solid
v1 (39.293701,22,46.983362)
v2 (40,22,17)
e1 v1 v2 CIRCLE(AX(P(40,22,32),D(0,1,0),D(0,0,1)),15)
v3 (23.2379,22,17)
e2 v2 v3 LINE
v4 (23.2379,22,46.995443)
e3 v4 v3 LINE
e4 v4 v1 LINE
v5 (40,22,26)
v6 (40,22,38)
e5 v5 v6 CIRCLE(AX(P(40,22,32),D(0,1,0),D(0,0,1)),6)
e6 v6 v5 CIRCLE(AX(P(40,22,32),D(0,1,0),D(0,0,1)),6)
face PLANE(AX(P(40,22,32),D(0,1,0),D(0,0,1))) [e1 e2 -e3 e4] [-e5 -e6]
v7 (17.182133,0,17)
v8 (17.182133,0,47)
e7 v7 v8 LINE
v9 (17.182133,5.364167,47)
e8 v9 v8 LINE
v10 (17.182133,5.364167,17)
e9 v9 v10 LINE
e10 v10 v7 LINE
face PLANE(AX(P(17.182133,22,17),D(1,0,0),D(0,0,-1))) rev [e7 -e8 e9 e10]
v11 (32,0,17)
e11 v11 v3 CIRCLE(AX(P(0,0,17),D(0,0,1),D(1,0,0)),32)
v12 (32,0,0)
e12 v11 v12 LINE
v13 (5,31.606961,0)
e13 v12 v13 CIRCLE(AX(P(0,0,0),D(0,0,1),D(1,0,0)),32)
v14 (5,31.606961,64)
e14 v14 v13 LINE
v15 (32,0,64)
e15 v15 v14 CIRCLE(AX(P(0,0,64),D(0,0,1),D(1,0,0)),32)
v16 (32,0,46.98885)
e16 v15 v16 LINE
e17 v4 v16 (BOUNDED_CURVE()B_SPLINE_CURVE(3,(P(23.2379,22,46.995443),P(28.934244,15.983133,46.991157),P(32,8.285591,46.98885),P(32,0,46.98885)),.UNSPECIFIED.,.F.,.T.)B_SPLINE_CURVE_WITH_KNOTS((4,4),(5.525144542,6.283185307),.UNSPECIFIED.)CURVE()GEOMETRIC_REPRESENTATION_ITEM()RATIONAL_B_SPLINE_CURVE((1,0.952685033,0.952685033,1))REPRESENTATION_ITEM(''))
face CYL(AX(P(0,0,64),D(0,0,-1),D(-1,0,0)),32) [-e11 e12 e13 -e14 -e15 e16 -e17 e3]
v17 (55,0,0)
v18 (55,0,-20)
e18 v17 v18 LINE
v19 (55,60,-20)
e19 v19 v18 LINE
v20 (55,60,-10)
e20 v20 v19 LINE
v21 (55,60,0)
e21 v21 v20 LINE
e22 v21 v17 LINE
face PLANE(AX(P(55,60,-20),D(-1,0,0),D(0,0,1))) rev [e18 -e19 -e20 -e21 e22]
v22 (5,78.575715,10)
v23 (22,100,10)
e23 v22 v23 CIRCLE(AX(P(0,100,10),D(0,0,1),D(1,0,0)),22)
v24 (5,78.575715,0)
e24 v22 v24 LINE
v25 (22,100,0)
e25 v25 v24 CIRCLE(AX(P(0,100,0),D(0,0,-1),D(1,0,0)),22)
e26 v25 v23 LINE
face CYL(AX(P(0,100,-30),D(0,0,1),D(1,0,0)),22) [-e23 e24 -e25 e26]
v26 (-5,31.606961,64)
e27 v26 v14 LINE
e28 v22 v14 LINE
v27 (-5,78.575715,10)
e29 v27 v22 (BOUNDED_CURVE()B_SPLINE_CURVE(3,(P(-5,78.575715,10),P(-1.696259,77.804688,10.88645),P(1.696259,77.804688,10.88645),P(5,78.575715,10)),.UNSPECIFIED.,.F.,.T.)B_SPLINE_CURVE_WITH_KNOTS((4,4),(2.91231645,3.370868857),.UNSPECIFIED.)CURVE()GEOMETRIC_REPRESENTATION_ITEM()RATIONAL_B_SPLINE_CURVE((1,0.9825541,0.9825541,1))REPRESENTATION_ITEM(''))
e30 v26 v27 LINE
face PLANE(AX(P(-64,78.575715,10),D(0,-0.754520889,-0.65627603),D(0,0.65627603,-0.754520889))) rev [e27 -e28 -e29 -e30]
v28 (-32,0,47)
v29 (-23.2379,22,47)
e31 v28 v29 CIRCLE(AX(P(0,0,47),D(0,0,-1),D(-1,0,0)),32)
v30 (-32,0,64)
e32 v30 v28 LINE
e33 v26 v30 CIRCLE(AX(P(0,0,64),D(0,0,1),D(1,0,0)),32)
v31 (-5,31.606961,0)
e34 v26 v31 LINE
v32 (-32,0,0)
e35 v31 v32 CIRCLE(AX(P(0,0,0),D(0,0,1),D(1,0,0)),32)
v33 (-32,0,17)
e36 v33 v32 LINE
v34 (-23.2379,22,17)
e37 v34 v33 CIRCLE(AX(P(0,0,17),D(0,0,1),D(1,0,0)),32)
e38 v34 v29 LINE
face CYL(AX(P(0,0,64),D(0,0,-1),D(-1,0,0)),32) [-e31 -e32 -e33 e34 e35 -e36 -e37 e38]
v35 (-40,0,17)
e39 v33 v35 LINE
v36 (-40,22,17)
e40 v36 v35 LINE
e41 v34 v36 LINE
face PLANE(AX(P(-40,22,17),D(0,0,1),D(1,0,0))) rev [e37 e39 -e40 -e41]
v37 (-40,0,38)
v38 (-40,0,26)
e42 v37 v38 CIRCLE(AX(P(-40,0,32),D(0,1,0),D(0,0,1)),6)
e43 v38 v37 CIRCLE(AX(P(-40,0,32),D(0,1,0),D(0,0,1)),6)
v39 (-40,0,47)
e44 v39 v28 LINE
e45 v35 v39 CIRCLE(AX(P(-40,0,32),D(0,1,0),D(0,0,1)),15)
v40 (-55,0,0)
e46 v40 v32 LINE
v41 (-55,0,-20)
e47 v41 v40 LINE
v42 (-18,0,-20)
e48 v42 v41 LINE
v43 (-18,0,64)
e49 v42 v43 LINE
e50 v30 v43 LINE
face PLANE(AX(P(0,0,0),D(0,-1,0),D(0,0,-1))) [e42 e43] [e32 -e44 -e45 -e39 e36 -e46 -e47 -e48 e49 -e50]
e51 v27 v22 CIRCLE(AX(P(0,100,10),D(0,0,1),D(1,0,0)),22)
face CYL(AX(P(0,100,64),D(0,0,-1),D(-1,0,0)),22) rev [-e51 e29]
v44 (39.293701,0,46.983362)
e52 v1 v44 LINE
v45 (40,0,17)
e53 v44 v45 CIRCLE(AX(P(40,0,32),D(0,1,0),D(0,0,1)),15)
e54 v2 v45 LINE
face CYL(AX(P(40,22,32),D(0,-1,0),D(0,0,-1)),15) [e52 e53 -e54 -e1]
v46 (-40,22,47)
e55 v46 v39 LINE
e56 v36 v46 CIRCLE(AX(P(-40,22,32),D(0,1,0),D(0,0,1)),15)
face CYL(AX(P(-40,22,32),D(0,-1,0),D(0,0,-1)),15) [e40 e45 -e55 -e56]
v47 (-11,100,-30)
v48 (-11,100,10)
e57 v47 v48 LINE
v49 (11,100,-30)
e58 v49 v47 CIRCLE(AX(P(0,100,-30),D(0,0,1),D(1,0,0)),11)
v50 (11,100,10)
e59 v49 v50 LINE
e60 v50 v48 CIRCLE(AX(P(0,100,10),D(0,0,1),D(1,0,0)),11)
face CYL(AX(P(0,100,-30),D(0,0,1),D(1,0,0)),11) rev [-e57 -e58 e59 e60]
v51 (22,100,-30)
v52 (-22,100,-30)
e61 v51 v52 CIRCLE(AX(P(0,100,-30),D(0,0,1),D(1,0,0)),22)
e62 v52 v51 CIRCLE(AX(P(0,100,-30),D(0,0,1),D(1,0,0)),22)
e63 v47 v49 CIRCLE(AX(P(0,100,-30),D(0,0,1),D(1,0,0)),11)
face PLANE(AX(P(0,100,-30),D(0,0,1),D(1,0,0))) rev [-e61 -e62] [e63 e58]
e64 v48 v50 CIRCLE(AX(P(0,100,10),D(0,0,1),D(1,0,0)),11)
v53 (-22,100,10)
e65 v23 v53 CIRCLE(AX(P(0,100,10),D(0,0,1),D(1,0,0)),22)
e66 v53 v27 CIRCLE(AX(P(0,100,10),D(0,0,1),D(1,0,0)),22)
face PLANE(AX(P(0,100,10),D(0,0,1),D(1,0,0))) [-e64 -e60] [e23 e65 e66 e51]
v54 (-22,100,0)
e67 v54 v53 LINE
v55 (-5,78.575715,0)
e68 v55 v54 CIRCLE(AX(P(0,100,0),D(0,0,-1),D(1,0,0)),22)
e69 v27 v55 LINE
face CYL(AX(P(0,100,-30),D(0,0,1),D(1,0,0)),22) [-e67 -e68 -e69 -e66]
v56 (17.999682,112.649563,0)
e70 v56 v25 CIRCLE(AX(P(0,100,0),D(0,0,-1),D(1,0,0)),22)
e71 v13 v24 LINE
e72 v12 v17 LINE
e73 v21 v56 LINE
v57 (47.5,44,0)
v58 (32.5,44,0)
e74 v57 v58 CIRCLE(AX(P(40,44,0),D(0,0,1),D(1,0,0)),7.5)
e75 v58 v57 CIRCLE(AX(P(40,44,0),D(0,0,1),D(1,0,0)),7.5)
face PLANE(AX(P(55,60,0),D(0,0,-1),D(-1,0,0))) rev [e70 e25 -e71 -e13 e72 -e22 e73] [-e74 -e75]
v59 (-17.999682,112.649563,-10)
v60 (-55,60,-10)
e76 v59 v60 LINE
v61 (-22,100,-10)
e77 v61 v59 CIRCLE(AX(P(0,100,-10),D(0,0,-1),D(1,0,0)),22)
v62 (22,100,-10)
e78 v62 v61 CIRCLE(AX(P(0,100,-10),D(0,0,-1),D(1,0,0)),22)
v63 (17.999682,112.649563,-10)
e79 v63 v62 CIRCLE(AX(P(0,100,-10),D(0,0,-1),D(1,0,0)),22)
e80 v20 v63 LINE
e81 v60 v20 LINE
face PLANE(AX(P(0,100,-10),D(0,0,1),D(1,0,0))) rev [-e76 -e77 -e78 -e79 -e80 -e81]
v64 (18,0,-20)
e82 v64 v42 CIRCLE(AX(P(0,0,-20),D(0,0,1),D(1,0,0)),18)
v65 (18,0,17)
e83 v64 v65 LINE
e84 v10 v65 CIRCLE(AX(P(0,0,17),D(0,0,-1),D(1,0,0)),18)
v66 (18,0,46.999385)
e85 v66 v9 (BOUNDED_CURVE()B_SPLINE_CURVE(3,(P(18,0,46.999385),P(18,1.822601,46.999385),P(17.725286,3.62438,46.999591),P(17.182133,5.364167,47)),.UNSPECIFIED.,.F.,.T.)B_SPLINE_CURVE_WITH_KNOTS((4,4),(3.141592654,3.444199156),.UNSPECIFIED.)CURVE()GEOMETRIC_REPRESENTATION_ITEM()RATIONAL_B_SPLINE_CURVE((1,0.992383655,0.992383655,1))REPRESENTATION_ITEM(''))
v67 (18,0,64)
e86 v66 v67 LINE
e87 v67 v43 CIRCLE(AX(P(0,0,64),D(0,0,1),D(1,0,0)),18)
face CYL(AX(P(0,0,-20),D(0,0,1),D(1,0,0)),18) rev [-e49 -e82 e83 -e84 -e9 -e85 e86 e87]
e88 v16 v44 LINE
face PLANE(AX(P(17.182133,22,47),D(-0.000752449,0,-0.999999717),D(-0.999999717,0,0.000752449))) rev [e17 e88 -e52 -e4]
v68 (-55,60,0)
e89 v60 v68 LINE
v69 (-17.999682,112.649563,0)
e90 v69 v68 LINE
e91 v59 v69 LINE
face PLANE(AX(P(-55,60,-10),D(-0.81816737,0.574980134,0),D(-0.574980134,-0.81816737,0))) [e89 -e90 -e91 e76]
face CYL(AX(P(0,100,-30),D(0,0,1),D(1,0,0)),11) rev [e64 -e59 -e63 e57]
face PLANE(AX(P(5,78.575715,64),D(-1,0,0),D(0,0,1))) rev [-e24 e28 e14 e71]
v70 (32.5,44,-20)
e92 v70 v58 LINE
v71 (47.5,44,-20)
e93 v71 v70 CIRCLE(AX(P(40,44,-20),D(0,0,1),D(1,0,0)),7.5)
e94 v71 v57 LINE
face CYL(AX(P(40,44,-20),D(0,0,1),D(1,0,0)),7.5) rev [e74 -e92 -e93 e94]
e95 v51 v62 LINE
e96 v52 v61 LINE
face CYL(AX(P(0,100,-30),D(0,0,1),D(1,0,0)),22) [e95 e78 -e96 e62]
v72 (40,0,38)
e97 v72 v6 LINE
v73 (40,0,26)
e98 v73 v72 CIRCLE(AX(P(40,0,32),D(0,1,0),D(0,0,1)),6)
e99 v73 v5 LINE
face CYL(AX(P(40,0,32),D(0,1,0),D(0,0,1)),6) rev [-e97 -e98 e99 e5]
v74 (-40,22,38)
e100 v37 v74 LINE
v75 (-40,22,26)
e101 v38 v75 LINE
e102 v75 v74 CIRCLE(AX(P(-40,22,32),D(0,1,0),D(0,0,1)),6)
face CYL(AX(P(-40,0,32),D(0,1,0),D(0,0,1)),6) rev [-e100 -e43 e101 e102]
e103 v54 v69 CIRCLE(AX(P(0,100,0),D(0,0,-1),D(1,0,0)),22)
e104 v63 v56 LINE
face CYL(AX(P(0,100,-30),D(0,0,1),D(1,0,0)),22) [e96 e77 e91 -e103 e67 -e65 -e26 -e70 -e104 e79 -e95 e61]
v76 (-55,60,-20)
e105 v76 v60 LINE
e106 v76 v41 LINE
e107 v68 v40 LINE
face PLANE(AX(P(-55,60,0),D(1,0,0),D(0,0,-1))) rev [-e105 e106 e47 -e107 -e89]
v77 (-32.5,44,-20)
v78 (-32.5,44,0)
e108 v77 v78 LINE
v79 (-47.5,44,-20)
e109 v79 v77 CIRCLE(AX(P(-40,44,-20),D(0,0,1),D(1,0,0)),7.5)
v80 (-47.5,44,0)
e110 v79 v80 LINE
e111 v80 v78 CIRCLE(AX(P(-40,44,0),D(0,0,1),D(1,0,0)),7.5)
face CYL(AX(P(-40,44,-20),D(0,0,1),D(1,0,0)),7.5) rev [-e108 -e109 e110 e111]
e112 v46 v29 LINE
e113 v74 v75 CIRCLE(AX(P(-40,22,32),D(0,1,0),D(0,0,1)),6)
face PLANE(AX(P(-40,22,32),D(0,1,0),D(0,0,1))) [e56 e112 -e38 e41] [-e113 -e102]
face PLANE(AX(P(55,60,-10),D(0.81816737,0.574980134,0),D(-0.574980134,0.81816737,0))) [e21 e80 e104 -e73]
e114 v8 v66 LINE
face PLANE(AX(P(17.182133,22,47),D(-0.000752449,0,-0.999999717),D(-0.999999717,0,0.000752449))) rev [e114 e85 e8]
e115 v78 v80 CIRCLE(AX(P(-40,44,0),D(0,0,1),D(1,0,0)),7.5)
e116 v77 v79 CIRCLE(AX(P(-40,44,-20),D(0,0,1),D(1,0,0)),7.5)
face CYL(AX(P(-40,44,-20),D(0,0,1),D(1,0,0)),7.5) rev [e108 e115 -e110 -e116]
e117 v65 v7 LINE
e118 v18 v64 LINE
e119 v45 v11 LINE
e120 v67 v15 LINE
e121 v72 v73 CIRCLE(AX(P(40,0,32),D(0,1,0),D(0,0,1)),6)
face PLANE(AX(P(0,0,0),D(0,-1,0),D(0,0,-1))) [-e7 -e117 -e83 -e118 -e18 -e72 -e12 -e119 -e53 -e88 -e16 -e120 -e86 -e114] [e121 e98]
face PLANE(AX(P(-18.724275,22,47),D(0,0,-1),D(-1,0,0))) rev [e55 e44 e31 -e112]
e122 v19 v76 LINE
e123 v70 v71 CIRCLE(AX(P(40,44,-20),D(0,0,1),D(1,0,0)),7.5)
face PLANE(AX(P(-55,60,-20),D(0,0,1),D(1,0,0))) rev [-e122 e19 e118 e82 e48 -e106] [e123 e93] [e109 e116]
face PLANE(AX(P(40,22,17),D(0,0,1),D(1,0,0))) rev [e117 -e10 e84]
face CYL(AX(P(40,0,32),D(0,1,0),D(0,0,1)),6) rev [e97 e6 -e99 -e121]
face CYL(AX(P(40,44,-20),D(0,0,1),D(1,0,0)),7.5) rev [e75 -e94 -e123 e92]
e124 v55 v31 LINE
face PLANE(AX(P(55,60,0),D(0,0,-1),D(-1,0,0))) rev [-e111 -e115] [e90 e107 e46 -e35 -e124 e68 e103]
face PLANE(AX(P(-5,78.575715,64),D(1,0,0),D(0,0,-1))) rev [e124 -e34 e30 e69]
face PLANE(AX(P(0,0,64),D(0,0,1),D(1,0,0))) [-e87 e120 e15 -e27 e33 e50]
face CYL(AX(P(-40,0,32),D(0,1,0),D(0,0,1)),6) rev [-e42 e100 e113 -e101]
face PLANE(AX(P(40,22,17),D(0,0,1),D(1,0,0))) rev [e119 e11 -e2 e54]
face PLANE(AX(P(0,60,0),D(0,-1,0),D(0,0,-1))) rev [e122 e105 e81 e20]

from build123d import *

# Parameters (mm, degrees)
BASE_BLOCK_SKETCH_W         = 110
BASE_BLOCK_SKETCH_H         = 20
BASE_BLOCK_DEPTH            = 60
BEARING_SADDLE_64_DEPTH     = 64
SADDLE_BORE_36_DEPTH        = 84
LEFT_MOUNTING_LUG_DEPTH     = 22
LEFT_LUG_HOLE_SKETCH_R      = 6
LEFT_LUG_HOLE_12_DEPTH      = 22
RIGHT_MOUNTING_LUG_DEPTH    = 22
RIGHT_LUG_HOLE_SKETCH_R     = 6
RIGHT_LUG_HOLE_12_DEPTH     = 22
UPRIGHT_PLATE_DEPTH         = 10
UPRIGHT_PLATE_DEPTH_BACK    = 30
UPRIGHT_PLATE_SKETCH_R      = 22
UPRIGHT_REINFORCEMENT_DEPTH = 10
UPPER_BORE_SKETCH_R         = 11
UPPER_BORE_22_DEPTH         = 40
GUSSET_BOSS_DEPTH           = 64
GUSSET_RELIEF_CUT_DEPTH     = 64
GUSSET_TRIM_CUT_DEPTH       = 10
UPRIGHT_HOLE_A_SKETCH_R     = 7.5
UPRIGHT_HOLE_A_15_DEPTH     = 20
UPRIGHT_HOLE_B_SKETCH_R     = 7.5
UPRIGHT_HOLE_B_15_DEPTH     = 20


with BuildPart() as part:
    # Base Block Sketch → Base Block (new body)
    with BuildSketch(Plane(origin=(0, 0, 0), x_dir=(1, 0, 0), z_dir=(0, 1, 0))):
        with Locations((0, 10)):
            Rectangle(BASE_BLOCK_SKETCH_W, BASE_BLOCK_SKETCH_H)
    extrude(amount=BASE_BLOCK_DEPTH)

    # Bearing Saddle Sketch → Bearing Saddle Ø64 (add)
    with BuildSketch(Plane.XY):
        with BuildLine():
            Line((-32, 0), (32, 0))
            ThreePointArc((32, 0), (0, 32), (-32, 0))
        make_face()
    extrude(amount=BEARING_SADDLE_64_DEPTH)

    # Saddle Bore Sketch → Saddle Bore Ø36 (cut)
    with BuildSketch(Plane.XY.offset(64)):
        with BuildLine():
            Line((-18, 0), (18, 0))
            ThreePointArc((18, 0), (0, 18), (-18, 0))
        make_face()
    extrude(amount=-SADDLE_BORE_36_DEPTH, mode=Mode.SUBTRACT)

    # Left Lug Sketch → Left Mounting Lug (add)
    with BuildSketch(Plane(origin=(0, 0, 0), x_dir=(1, 0, 0), z_dir=(0, 1, 0))):
        with BuildLine():
            Line((-40, -17), (-18.724275485, -17))
            Line((-18.724275485, -17), (-18.724275485, -47))
            Line((-18.724275485, -47), (-40, -47))
            ThreePointArc((-40, -47), (-55, -32), (-40, -17))
        make_face()
    extrude(amount=LEFT_MOUNTING_LUG_DEPTH)

    # Left Lug Hole Sketch → Left Lug Hole Ø12 (cut)
    with BuildSketch(Plane(origin=(0, 22, 0), x_dir=(1, 0, 0), z_dir=(0, 1, 0))):
        with Locations(Location((-40, -32, 0), (0, 0, 270))):
            Circle(LEFT_LUG_HOLE_SKETCH_R)
    extrude(amount=-LEFT_LUG_HOLE_12_DEPTH, mode=Mode.SUBTRACT)

    # Right Lug Sketch → Right Mounting Lug (add)
    with BuildSketch(Plane(origin=(0, 0, 0), x_dir=(1, 0, 0), z_dir=(0, 1, 0))):
        with BuildLine():
            Line((40, -17), (17.182133471, -17))
            Line((17.182133471, -17), (17.182133471, -47))
            Line((17.182133471, -47), (39.293701119, -46.983362169))
            ThreePointArc((39.293701119, -46.983362169), (54.995839965, -32.353247409), (40, -17))
        make_face()
    extrude(amount=RIGHT_MOUNTING_LUG_DEPTH)

    # Right Lug Hole Sketch → Right Lug Hole Ø12 (cut)
    with BuildSketch(Plane(origin=(0, 22, 0), x_dir=(1, 0, 0), z_dir=(0, 1, 0))):
        with Locations(Location((40, -32, 0), (0, 0, 270))):
            Circle(RIGHT_LUG_HOLE_SKETCH_R)
    extrude(amount=-RIGHT_LUG_HOLE_12_DEPTH, mode=Mode.SUBTRACT)



with BuildPart() as body_2:
    # Upright Plate Sketch → Upright Plate (new, two sides: drawn at the far end of the back side and taken through both)
    with BuildSketch(Plane.XY.offset(-UPRIGHT_PLATE_DEPTH_BACK)):
        with Locations((0, 100)):
            Circle(UPRIGHT_PLATE_SKETCH_R)
    extrude(amount=UPRIGHT_PLATE_DEPTH + UPRIGHT_PLATE_DEPTH_BACK)


with BuildPart() as part_1:
    add(part.part)

    add(body_2.part)  # Upright Reinforcement merges body 2
    # Upright Reinforcement Sketch → Upright Reinforcement (add)
    with BuildSketch(Plane.XY):
        with BuildLine():
            Line((-55, 60), (-17.999682143, 112.649562947))
            ThreePointArc((-17.999682143, 112.649562947), (0, 78), (17.999682143, 112.649562947))
            Line((17.999682143, 112.649562947), (55, 60))
            Line((55, 60), (-55, 60))
        make_face()
    extrude(amount=-UPRIGHT_REINFORCEMENT_DEPTH)

    # Upper Bore Sketch → Upper Bore Ø22 (cut)
    with BuildSketch(Plane.XY.offset(10)):
        with Locations((0, 100)):
            Circle(UPPER_BORE_SKETCH_R)
    extrude(amount=-UPPER_BORE_22_DEPTH, mode=Mode.SUBTRACT)

    # Gusset Boss Sketch → Gusset Boss (add)
    with BuildSketch(Plane.XY):
        with BuildLine():
            Line((-5, 78.575714714), (-5, 31.606961259))
            ThreePointArc((-5, 31.606961259), (0, 32), (5, 31.606961259))
            Line((5, 31.606961259), (5, 78.575714714))
            ThreePointArc((5, 78.575714714), (0, 78), (-5, 78.575714714))
        make_face()
    extrude(amount=GUSSET_BOSS_DEPTH)

    # Gusset Relief Sketch → Gusset Relief Cut (cut)
    with BuildSketch(Plane(origin=(0, 0, 0), x_dir=(0, 0, -1), z_dir=(1, 0, 0))):
        Polygon((-10, 78.575714714), (-64, 31.606961259), (-64, 78.575714714), align=None)
    extrude(amount=-GUSSET_RELIEF_CUT_DEPTH, mode=Mode.SUBTRACT)

    # Gusset Trim Sketch → Gusset Trim Cut (cut)
    with BuildSketch(Plane.ZY):
        Polygon((10, 78.575714714), (64, 31.606961259), (64, 78.575714714), align=None)
    extrude(amount=-GUSSET_TRIM_CUT_DEPTH, mode=Mode.SUBTRACT)

    # Upright Hole A Sketch → Upright Hole A Ø15 (cut)
    with BuildSketch(Plane.XY):
        with Locations((40, 44)):
            Circle(UPRIGHT_HOLE_A_SKETCH_R)
    extrude(amount=-UPRIGHT_HOLE_A_15_DEPTH, mode=Mode.SUBTRACT)

    # Upright Hole B Sketch → Upright Hole B Ø15 (cut)
    with BuildSketch(Plane.XY):
        with Locations((-40, 44)):
            Circle(UPRIGHT_HOLE_B_SKETCH_R)
    extrude(amount=-UPRIGHT_HOLE_B_15_DEPTH, mode=Mode.SUBTRACT)


solid = part_1.part
